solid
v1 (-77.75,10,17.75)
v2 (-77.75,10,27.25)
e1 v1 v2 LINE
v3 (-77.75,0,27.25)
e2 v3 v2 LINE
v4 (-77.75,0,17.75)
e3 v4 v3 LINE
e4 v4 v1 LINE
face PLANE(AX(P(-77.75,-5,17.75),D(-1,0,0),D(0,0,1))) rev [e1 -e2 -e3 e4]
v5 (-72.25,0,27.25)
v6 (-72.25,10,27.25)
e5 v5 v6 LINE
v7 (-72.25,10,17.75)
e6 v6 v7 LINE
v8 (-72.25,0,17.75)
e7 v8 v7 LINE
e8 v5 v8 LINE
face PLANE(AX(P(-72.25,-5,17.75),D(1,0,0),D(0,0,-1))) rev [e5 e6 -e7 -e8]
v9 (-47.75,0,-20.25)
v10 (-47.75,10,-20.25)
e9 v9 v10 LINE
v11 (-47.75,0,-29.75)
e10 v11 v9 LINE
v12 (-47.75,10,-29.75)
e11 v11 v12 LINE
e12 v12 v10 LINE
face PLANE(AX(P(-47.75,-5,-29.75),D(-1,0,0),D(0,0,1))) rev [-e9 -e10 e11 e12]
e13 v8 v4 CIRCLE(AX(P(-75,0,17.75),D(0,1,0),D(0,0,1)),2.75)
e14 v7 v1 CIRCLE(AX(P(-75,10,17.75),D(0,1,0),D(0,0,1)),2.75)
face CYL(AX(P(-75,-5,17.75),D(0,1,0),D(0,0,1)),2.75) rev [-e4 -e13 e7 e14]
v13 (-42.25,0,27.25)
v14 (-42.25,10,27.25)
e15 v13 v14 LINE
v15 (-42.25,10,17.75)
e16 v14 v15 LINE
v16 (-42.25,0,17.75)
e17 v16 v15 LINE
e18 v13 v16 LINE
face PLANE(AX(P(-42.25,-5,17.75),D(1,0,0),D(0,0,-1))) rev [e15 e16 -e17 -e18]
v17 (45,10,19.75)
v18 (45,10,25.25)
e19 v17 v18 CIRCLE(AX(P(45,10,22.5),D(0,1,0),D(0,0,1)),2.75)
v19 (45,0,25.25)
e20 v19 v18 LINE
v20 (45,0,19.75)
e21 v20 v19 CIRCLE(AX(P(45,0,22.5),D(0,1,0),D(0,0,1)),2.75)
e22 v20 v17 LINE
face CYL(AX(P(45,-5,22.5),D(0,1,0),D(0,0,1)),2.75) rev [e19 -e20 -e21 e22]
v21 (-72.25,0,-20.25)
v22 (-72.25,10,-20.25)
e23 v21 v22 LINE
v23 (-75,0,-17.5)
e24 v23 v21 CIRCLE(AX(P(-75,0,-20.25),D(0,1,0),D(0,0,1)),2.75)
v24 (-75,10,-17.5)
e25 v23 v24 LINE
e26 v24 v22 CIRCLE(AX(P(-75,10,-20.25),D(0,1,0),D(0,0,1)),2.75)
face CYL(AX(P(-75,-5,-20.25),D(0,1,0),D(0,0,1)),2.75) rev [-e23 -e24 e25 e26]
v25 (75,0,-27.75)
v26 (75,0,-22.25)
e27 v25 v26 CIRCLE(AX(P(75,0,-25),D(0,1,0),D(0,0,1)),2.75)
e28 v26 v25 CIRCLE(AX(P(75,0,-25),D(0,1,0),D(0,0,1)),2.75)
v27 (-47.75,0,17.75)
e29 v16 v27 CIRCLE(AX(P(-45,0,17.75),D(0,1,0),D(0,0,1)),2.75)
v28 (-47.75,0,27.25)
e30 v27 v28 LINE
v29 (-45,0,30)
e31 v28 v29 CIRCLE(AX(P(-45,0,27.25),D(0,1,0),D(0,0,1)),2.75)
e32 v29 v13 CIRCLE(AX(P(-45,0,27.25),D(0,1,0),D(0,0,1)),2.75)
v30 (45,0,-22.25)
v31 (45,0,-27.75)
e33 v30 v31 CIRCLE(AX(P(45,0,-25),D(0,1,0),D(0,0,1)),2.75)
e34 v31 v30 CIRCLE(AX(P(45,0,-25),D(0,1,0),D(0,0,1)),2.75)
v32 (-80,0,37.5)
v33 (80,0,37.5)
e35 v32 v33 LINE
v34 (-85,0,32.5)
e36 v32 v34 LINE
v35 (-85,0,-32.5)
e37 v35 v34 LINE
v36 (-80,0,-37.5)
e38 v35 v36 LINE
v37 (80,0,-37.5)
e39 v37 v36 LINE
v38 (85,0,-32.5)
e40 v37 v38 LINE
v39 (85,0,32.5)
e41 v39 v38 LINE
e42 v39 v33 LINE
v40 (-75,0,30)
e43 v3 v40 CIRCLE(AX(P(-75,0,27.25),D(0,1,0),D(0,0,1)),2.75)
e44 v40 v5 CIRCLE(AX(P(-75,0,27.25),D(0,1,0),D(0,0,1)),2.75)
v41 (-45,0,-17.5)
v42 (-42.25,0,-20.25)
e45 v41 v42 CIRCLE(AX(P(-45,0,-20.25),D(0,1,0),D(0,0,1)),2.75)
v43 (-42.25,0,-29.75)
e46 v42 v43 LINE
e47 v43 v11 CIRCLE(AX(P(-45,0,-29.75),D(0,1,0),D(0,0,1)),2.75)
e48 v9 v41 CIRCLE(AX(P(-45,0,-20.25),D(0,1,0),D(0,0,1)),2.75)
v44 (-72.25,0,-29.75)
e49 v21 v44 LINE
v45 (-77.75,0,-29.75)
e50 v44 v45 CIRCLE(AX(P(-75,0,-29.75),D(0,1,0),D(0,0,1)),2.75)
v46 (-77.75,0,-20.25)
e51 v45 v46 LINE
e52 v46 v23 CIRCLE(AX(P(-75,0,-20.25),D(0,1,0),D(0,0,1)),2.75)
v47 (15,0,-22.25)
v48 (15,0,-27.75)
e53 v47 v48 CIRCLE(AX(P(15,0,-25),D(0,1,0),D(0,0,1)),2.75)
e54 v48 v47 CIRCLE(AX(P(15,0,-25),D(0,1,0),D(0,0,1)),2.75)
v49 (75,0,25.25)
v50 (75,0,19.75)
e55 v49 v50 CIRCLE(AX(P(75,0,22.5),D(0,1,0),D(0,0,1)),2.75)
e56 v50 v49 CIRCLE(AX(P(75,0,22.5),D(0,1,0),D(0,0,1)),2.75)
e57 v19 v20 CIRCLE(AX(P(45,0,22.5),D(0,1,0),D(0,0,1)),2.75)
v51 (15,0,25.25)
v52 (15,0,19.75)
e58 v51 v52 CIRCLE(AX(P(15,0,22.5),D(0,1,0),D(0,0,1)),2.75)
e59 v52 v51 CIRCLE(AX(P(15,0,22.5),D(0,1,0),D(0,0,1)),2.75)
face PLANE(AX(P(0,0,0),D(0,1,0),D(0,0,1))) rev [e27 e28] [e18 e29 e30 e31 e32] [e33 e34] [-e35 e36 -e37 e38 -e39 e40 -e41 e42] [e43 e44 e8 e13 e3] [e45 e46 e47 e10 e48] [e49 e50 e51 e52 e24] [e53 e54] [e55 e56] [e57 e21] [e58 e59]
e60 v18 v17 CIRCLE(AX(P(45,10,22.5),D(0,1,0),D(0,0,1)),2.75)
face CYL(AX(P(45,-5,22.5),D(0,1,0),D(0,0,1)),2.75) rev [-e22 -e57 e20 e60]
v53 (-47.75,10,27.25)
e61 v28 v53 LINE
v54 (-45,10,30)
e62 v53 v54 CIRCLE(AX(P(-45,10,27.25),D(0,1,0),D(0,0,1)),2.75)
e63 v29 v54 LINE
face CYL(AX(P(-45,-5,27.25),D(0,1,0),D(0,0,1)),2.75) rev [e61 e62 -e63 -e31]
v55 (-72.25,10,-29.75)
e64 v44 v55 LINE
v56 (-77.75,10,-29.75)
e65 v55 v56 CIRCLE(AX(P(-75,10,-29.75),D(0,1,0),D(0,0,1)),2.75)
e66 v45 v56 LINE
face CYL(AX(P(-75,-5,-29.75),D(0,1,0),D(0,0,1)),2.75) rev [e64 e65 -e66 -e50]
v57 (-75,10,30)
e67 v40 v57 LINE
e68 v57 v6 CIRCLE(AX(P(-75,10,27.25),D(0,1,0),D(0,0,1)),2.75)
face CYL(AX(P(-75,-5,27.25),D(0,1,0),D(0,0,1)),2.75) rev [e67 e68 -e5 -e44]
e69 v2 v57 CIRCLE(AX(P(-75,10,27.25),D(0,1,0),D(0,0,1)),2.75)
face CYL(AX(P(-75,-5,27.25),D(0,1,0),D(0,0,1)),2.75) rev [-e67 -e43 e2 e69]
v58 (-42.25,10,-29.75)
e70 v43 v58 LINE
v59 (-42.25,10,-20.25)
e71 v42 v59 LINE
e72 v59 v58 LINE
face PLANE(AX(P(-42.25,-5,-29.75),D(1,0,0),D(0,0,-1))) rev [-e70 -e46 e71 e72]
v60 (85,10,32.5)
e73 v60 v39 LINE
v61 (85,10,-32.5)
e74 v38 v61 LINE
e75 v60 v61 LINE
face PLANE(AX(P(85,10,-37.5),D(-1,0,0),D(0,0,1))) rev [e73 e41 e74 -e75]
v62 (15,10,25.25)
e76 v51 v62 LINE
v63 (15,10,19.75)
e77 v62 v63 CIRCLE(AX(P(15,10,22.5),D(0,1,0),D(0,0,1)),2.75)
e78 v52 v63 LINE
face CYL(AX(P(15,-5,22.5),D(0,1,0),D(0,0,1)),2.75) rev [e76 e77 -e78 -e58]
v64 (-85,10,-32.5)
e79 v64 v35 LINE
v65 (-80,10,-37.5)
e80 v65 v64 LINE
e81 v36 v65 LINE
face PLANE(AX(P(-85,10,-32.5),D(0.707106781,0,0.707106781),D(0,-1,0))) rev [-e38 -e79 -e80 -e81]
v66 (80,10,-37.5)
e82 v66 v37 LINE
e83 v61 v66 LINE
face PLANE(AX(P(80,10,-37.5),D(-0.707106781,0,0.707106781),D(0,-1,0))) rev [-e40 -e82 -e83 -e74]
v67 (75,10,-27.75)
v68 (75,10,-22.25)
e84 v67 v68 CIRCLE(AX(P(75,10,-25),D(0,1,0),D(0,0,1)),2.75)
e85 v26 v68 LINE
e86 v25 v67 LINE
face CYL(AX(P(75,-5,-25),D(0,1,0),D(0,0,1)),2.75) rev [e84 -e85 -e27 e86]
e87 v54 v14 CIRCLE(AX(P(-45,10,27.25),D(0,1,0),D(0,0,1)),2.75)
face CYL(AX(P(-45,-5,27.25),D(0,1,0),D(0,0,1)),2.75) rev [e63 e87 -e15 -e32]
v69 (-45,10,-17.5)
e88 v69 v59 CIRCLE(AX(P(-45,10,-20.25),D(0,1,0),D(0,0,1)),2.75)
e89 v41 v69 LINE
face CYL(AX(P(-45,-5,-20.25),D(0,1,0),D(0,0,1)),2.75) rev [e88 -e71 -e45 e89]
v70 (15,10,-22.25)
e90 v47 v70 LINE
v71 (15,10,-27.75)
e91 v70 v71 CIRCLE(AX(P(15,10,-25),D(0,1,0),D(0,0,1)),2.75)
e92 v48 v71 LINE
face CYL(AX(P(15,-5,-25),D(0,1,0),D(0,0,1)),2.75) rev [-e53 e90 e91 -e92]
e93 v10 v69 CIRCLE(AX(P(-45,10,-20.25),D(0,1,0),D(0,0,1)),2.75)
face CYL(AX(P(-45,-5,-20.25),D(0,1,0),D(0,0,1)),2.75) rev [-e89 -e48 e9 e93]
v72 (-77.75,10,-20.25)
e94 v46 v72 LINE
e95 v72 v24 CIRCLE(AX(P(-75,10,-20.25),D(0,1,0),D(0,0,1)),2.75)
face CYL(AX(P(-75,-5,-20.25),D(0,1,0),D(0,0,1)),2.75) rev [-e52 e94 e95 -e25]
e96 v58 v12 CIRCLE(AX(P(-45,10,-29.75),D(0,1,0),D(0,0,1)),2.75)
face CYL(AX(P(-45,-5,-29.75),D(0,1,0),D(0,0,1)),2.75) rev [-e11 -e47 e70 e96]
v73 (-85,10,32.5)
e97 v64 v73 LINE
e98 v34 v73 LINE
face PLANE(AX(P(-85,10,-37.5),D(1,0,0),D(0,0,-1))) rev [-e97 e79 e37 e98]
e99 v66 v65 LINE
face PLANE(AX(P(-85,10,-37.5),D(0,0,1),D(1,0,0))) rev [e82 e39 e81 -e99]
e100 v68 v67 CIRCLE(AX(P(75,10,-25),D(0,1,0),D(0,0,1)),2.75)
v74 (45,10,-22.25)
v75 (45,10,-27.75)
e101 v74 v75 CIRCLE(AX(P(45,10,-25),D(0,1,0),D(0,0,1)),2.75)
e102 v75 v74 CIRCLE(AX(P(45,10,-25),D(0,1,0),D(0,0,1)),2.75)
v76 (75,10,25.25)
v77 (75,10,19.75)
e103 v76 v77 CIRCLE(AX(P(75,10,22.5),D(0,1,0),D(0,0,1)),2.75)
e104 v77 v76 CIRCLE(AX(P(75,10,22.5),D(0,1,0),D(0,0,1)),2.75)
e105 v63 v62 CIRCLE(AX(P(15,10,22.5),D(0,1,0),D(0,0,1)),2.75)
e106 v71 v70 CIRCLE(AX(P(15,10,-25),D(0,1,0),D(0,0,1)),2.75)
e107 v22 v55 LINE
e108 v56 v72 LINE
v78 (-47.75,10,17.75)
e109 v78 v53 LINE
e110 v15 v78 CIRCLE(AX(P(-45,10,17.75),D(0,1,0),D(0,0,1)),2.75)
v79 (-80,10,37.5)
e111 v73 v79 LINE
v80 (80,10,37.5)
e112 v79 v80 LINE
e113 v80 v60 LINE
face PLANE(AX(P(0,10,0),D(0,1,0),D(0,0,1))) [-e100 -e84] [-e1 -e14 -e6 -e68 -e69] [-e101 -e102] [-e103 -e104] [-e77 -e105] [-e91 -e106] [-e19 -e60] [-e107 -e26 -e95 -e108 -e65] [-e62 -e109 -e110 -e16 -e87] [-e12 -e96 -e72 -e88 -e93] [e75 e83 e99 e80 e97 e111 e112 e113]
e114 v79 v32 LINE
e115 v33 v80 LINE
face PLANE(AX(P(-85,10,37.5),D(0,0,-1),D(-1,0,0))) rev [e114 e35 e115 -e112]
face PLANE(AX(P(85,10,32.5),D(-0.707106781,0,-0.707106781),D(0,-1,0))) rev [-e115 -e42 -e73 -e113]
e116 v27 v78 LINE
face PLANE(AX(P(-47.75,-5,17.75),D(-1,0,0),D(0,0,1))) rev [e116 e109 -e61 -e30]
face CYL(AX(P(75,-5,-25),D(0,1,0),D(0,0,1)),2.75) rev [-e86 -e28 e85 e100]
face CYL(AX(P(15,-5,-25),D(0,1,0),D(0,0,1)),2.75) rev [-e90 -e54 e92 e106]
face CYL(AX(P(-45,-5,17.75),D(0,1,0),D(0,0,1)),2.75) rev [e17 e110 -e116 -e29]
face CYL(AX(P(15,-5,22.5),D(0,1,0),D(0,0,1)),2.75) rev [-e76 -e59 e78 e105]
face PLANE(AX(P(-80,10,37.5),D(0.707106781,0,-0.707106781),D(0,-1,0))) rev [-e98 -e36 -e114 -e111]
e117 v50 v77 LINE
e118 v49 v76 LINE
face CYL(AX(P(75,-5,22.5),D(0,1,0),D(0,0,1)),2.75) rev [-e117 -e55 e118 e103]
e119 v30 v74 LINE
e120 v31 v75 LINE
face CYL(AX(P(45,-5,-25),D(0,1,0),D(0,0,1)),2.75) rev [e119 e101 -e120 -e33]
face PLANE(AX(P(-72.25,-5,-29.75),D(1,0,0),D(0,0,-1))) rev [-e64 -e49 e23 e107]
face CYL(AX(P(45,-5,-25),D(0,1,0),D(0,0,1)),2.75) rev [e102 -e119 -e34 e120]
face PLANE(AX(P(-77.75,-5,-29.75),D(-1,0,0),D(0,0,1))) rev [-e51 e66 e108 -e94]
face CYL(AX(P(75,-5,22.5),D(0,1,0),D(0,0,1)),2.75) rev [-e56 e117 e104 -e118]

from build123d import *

# Parameters (mm, degrees)
SKETCH_1_W          = 170
SKETCH_1_H          = 75
EXTRUDE_1_DEPTH     = 10
CHAMFER_1_SIZE      = 5
SKETCH_2_R          = 2.75
CUT_EXTRUDE_1_DEPTH = 15


with BuildPart() as part:
    # 草图1 → 凸台-拉伸1 (new body)
    with BuildSketch(Plane(origin=(0, 0, 0), x_dir=(1, 0, 0), z_dir=(0, 1, 0))):
        Rectangle(SKETCH_1_W, SKETCH_1_H)
    extrude(amount=EXTRUDE_1_DEPTH)

    # 倒角1
    chamfer_1_edges = [part.edges().sort_by_distance(p)[0] for p in [
        (85, 5, 37.5),
        (-85, 5, 37.5),
        (-85, 5, -37.5),
        (85, 5, -37.5),
    ]]
    chamfer(chamfer_1_edges, length=CHAMFER_1_SIZE)

    # 草图2 → 切除-拉伸1 (cut)
    with BuildSketch(Plane(origin=(0, 10, 0), x_dir=(1, 0, 0), z_dir=(0, 1, 0))):
        with Locations(Location((15, 25, 0), (0, 0, 270))):
            Circle(SKETCH_2_R)
        with Locations(Location((45, 25, 0), (0, 0, 270))):
            Circle(SKETCH_2_R)
        with Locations(Location((75, 25, 0), (0, 0, 270))):
            Circle(SKETCH_2_R)
        with Locations(Location((15, -22.5, 0), (0, 0, 270))):
            Circle(SKETCH_2_R)
        with Locations(Location((45, -22.5, 0), (0, 0, 270))):
            Circle(SKETCH_2_R)
        with Locations(Location((75, -22.5, 0), (0, 0, 270))):
            Circle(SKETCH_2_R)
        with BuildLine():
            Line((-72.25, 29.75), (-72.25, 20.25))
            ThreePointArc((-72.25, 20.25), (-75, 17.5), (-77.75, 20.25))
            Line((-77.75, 20.25), (-77.75, 29.75))
            ThreePointArc((-77.75, 29.75), (-75, 32.5), (-72.25, 29.75))
        make_face()
        with BuildLine():
            Line((-42.25, 29.75), (-42.25, 20.25))
            ThreePointArc((-42.25, 20.25), (-45, 17.5), (-47.75, 20.25))
            Line((-47.75, 20.25), (-47.75, 29.75))
            ThreePointArc((-47.75, 29.75), (-45, 32.5), (-42.25, 29.75))
        make_face()
        with BuildLine():
            Line((-72.25, -17.75), (-72.25, -27.25))
            ThreePointArc((-72.25, -27.25), (-75, -30), (-77.75, -27.25))
            Line((-77.75, -27.25), (-77.75, -17.75))
            ThreePointArc((-77.75, -17.75), (-75, -15), (-72.25, -17.75))
        make_face()
        with BuildLine():
            Line((-42.25, -17.75), (-42.25, -27.25))
            ThreePointArc((-42.25, -27.25), (-45, -30), (-47.75, -27.25))
            Line((-47.75, -27.25), (-47.75, -17.75))
            ThreePointArc((-47.75, -17.75), (-45, -15), (-42.25, -17.75))
        make_face()
    extrude(amount=-CUT_EXTRUDE_1_DEPTH, mode=Mode.SUBTRACT)


solid = part.part
